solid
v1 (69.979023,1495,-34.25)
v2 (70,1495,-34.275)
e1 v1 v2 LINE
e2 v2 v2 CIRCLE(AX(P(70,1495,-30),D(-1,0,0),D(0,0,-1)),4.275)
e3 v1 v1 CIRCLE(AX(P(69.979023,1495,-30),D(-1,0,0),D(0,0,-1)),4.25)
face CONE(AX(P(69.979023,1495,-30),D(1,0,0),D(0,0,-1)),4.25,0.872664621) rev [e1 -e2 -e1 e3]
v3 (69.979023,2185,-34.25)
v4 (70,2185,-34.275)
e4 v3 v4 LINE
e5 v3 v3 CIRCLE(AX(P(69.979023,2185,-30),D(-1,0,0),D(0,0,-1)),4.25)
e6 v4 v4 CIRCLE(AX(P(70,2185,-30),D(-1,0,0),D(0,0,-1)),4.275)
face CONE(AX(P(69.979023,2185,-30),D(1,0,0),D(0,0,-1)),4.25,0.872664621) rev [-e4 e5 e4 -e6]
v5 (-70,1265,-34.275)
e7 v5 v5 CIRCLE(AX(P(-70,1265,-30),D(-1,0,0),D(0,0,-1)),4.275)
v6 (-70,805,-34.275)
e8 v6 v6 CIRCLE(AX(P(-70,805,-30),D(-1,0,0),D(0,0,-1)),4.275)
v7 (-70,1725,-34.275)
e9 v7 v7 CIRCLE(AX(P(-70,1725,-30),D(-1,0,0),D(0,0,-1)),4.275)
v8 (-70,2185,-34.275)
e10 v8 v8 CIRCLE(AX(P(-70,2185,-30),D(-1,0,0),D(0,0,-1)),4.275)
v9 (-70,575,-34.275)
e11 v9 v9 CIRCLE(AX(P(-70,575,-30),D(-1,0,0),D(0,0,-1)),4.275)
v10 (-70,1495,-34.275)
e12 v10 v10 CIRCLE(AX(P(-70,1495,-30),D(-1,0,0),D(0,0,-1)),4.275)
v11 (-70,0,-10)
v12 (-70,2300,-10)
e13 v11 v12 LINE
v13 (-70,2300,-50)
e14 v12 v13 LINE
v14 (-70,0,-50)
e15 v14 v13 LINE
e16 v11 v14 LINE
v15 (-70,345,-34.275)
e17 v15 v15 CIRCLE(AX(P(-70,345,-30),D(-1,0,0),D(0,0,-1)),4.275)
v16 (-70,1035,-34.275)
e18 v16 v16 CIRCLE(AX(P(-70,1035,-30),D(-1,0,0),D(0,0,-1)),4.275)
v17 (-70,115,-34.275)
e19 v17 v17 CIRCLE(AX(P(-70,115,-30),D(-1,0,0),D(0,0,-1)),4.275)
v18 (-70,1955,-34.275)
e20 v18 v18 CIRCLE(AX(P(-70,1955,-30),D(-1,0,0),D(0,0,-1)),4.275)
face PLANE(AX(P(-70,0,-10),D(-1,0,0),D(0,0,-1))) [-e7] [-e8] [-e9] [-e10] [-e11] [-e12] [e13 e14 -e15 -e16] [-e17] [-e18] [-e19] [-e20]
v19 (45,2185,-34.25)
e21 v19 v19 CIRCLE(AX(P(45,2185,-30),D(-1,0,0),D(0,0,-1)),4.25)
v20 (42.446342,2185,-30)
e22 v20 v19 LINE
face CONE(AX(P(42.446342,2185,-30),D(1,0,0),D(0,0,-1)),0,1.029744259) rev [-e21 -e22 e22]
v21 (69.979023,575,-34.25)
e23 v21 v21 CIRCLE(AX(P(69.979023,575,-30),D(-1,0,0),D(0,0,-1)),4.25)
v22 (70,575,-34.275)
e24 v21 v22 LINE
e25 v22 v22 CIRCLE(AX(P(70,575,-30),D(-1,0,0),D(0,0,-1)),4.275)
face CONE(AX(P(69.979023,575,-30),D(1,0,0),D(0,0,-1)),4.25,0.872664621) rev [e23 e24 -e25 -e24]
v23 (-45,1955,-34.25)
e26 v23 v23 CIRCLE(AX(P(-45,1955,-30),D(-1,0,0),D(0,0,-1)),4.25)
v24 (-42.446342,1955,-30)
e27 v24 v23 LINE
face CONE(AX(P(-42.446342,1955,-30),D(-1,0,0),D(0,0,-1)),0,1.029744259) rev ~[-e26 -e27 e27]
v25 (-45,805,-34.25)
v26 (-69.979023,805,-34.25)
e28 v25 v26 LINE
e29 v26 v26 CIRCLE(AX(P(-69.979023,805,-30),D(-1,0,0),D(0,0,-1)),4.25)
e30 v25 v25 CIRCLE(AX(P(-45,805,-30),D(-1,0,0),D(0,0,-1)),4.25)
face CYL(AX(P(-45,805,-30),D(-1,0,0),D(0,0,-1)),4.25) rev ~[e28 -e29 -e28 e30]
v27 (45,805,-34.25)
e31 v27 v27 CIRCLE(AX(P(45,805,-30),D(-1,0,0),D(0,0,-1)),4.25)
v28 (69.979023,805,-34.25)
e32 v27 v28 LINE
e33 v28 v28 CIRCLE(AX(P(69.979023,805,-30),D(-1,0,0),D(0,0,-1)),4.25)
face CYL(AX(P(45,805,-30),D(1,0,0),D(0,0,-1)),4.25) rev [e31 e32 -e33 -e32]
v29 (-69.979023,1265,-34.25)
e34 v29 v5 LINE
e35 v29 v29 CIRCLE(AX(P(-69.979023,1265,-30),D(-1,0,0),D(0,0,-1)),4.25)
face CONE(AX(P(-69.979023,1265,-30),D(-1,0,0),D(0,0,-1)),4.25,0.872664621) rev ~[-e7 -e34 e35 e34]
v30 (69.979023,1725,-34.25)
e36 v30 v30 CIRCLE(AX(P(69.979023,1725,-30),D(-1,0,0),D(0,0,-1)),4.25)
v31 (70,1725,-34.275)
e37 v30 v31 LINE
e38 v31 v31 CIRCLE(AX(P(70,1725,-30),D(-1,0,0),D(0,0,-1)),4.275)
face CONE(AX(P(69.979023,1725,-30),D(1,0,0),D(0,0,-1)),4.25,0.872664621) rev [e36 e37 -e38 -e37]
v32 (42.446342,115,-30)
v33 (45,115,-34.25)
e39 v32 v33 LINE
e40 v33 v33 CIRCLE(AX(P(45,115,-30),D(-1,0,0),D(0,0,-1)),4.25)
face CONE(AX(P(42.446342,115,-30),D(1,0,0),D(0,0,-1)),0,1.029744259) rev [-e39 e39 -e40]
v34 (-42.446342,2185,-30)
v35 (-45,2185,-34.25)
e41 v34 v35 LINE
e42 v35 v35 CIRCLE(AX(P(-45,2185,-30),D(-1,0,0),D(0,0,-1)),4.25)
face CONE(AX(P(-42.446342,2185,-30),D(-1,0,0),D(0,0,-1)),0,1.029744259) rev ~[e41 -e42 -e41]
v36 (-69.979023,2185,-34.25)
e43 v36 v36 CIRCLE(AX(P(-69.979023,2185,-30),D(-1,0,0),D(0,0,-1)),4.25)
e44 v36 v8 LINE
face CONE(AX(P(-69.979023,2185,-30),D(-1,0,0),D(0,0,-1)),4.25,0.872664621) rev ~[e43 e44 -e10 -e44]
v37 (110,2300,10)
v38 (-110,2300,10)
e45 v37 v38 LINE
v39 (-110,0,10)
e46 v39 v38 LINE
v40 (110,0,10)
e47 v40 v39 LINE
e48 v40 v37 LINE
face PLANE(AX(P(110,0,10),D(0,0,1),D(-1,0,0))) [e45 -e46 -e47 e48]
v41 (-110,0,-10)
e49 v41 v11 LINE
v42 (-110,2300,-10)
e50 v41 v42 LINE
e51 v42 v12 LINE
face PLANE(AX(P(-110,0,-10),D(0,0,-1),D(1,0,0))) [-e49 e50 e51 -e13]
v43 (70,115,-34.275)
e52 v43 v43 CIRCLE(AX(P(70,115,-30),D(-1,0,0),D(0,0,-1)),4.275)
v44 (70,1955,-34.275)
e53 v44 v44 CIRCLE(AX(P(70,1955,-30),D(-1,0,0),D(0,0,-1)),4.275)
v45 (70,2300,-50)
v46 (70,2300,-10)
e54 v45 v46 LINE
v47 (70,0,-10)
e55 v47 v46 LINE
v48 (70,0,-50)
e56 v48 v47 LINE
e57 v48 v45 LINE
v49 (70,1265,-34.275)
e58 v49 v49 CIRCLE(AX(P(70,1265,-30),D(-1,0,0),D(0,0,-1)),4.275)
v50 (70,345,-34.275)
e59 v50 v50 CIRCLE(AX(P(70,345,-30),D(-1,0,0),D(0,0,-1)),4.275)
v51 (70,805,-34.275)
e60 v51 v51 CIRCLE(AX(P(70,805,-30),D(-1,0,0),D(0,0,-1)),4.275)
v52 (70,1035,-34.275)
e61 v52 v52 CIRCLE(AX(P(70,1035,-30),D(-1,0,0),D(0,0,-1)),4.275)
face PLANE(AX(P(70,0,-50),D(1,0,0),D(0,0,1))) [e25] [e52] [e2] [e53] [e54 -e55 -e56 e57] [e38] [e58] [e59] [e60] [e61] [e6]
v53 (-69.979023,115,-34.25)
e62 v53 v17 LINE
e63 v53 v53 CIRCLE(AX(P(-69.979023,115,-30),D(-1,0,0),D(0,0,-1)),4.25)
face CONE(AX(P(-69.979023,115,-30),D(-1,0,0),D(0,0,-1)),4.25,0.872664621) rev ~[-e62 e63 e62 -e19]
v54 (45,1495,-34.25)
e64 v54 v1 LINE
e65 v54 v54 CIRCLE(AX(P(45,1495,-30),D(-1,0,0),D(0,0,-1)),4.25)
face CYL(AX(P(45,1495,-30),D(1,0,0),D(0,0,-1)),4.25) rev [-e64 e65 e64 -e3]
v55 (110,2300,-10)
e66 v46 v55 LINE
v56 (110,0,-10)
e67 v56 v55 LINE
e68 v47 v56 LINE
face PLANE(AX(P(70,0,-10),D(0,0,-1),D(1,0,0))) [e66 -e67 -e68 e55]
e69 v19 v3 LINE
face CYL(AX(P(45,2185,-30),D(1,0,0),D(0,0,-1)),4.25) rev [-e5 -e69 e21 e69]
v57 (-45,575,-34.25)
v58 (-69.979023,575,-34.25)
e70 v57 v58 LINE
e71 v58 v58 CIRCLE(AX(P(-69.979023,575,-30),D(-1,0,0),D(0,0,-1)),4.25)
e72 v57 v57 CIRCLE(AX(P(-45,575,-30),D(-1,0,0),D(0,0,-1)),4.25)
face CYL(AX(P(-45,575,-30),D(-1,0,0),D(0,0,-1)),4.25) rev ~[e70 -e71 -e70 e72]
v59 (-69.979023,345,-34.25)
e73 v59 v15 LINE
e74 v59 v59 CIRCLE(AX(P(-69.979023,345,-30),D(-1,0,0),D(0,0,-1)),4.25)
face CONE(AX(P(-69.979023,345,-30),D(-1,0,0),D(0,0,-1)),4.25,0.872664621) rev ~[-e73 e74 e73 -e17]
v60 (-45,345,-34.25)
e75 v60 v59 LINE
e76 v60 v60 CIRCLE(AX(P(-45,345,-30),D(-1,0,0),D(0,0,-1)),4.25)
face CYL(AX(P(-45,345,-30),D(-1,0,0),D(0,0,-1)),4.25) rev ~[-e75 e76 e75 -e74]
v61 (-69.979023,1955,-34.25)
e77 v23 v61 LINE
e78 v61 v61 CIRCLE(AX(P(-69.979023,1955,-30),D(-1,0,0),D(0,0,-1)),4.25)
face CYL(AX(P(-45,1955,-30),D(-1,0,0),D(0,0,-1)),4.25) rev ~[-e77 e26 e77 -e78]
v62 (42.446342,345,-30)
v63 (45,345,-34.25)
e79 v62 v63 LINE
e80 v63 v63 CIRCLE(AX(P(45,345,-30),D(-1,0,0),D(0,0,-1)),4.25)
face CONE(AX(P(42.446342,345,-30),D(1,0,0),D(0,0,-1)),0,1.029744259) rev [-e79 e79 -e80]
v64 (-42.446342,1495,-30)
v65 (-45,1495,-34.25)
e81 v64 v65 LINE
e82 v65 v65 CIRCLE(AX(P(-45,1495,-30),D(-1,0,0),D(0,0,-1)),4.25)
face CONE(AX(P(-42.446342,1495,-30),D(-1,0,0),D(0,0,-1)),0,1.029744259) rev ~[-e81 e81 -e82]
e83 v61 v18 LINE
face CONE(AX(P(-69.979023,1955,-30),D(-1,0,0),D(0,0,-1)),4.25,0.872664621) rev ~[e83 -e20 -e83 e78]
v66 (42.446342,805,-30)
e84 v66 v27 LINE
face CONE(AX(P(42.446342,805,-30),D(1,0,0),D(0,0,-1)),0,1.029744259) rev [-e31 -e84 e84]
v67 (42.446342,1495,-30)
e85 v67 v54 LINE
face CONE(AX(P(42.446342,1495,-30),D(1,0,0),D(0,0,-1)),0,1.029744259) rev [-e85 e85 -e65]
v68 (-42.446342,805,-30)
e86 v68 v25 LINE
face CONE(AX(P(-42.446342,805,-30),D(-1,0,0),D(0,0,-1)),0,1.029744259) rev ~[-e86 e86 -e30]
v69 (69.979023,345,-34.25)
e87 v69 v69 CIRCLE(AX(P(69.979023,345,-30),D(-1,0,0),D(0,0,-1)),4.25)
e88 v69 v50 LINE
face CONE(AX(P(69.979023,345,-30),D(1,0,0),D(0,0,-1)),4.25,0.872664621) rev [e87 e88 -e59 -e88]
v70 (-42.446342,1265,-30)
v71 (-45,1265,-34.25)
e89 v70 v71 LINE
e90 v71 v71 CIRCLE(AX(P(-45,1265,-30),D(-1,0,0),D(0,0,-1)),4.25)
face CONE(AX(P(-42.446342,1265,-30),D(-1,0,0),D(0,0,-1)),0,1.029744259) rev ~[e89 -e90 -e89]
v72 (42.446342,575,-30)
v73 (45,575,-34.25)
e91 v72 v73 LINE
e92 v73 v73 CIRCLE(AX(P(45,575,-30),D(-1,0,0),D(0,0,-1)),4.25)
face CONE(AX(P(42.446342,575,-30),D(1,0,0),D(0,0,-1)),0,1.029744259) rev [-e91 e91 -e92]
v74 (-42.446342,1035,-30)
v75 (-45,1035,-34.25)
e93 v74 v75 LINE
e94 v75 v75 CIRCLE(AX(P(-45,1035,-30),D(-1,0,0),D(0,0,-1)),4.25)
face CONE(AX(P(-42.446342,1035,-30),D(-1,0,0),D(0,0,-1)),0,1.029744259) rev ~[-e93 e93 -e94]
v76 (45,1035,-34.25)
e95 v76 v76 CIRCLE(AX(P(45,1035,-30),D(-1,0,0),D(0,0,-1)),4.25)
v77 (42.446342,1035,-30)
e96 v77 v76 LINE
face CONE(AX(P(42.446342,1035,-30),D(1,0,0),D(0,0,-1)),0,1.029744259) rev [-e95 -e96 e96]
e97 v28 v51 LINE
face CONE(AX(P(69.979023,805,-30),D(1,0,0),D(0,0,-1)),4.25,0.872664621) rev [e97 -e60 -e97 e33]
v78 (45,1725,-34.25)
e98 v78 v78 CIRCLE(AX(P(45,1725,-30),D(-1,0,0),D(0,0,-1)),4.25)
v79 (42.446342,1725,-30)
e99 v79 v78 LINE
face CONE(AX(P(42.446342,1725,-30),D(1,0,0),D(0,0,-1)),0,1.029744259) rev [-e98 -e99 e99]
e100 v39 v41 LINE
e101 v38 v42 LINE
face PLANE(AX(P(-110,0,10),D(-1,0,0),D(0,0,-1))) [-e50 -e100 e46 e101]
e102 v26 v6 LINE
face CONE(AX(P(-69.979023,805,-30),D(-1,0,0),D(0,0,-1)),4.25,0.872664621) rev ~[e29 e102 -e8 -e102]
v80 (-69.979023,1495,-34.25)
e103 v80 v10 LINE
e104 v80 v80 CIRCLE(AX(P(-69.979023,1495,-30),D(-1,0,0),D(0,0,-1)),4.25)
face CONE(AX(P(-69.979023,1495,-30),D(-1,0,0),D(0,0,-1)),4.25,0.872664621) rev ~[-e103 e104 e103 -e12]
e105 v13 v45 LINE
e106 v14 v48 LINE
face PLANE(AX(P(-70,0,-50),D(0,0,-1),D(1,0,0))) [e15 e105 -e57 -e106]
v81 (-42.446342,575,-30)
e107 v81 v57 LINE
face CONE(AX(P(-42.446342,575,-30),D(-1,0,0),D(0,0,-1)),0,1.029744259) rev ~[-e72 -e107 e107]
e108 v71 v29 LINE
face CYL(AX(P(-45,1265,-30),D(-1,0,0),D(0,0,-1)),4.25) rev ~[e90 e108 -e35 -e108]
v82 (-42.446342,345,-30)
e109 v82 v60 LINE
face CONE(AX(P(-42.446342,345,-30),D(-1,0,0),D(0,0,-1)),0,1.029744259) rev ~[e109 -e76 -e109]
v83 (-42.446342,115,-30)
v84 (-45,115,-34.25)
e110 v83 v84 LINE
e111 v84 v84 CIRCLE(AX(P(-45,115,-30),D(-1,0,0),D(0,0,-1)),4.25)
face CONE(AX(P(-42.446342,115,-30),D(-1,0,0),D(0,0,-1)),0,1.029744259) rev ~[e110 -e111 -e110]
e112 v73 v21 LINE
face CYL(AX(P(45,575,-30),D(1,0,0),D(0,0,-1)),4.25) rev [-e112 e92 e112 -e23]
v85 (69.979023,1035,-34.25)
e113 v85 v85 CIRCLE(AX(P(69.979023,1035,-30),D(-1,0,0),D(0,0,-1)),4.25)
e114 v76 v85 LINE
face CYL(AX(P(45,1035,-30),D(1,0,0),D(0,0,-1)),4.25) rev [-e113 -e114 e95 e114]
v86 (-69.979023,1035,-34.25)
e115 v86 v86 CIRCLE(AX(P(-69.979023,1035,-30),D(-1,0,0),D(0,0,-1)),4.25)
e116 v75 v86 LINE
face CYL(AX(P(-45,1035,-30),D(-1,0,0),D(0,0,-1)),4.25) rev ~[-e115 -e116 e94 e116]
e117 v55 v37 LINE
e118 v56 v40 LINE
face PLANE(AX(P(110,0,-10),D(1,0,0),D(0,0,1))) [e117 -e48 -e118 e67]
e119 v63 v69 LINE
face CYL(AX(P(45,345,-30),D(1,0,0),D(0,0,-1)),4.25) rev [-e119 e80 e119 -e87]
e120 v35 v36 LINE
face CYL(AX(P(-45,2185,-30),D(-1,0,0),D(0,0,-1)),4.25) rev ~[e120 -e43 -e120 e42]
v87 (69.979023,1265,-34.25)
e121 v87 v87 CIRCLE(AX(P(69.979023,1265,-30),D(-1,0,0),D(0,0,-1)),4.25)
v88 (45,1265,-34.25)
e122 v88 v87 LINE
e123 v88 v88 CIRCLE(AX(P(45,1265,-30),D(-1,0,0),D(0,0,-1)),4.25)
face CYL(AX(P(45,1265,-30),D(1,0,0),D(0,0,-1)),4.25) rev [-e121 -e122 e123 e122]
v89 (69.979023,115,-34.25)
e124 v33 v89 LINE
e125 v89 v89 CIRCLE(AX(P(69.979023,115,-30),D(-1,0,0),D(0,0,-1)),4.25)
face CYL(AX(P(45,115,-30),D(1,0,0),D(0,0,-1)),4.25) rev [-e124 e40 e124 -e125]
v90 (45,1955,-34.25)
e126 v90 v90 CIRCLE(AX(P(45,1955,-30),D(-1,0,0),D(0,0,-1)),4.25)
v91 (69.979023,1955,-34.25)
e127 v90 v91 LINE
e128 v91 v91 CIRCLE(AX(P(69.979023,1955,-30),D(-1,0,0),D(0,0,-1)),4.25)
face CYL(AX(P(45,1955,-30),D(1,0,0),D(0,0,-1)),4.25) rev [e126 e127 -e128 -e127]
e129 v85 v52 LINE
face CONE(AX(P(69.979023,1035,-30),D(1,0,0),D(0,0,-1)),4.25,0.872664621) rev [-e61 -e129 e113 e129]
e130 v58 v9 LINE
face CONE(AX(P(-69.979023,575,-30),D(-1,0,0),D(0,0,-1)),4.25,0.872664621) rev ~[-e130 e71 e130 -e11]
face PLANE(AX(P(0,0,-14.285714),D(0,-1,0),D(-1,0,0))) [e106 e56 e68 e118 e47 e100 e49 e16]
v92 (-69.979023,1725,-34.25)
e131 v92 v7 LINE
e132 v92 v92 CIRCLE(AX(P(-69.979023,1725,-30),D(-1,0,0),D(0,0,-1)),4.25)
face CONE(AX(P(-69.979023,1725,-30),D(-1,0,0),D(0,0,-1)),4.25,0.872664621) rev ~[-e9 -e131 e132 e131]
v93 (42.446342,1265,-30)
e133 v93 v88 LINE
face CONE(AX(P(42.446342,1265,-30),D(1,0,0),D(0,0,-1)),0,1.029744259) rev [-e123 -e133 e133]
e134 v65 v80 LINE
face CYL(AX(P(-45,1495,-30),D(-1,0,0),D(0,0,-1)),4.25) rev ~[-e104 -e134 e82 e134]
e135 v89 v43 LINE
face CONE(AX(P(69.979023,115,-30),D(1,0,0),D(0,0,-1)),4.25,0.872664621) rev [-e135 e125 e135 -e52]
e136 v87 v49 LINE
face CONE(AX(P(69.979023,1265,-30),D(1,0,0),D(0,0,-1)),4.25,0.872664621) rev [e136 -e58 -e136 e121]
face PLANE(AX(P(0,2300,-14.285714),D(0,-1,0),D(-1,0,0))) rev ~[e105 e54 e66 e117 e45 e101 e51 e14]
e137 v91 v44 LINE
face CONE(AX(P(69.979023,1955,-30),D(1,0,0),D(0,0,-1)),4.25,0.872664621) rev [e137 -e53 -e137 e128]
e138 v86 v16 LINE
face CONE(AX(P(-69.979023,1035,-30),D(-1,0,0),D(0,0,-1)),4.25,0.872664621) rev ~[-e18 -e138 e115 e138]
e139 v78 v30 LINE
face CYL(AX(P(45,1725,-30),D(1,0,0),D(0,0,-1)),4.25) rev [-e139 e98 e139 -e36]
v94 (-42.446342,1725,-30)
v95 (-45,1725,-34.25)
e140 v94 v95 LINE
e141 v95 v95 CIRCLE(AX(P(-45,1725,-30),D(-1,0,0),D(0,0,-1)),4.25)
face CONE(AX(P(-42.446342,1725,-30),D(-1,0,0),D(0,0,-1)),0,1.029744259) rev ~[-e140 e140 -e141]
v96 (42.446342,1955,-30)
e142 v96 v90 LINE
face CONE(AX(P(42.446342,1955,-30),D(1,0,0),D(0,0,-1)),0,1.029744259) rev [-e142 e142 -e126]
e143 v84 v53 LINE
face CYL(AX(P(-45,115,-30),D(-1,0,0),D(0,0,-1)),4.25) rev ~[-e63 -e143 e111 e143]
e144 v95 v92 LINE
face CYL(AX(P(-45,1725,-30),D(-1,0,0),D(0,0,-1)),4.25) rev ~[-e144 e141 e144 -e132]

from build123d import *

# Parameters (mm, degrees)
BOSS_EXTRUDE1_DEPTH = 2300
LPATTERN1_COUNT     = 10
LPATTERN1_PITCH     = 230


with BuildPart() as part:
    # Sketch1 → Boss-Extrude1 (new body)
    with BuildSketch(Plane(origin=(0, 0, 0), x_dir=(1, 0, 0), z_dir=(0, 1, 0))):
        Polygon((-70, 10), (-70, 50), (70, 50), (70, 10), (110, 10), (110, -10), (-110, -10), (-110, 10), align=None)
    extrude(amount=BOSS_EXTRUDE1_DEPTH)

    # Sketch3 → Tap Drill for M10 Tap1 (revolve, cut)
    with BuildSketch(Plane(origin=(70, 2185, -30), x_dir=(0, 0, -1), z_dir=(0, 1, 0))):
        Polygon((0, 0), (0, 27.553657631), (4.25, 25), (4.25, 0.020977491), (4.275, 0), align=None)
    tap_drill_for_m10_tap1 = revolve(axis=Axis((76.35, 2185, -30), (-1, 0, 0)), mode=Mode.SUBTRACT)

    # LPattern1: Tap Drill for M10 Tap1 ×10
    with Locations(*[(0, -i * LPATTERN1_PITCH, 0) for i in range(1, LPATTERN1_COUNT)]):
        add(tap_drill_for_m10_tap1, mode=Mode.SUBTRACT)

    # Mirror1: Tap Drill for M10 Tap1 across plane
    add(tap_drill_for_m10_tap1.mirror(Plane(origin=(0, 0, 0), x_dir=(0, 0, 1), z_dir=(1, 0, 0))), mode=Mode.SUBTRACT)

    # Mirror1 copy 1 sketch → Mirror1 copy 1 (revolve, cut)
    with BuildSketch(Plane(origin=(-70, 1955, -30), x_dir=(0, 0, -1), z_dir=(0, 1, 0))):
        Polygon((0, 0), (0, -27.553657631), (4.25, -25), (4.25, -0.020977491), (4.275, 0), align=None)
    revolve(axis=Axis((-76.35, 1955, -30), (-1, 0, 0)), mode=Mode.SUBTRACT)

    # Mirror1 copy 2 sketch → Mirror1 copy 2 (revolve, cut)
    with BuildSketch(Plane(origin=(-70, 1725, -30), x_dir=(0, 0, -1), z_dir=(0, 1, 0))):
        Polygon((0, 0), (0, -27.553657631), (4.25, -25), (4.25, -0.020977491), (4.275, 0), align=None)
    revolve(axis=Axis((-76.35, 1725, -30), (-1, 0, 0)), mode=Mode.SUBTRACT)

    # Mirror1 copy 3 sketch → Mirror1 copy 3 (revolve, cut)
    with BuildSketch(Plane(origin=(-70, 1495, -30), x_dir=(0, 0, -1), z_dir=(0, 1, 0))):
        Polygon((0, 0), (0, -27.553657631), (4.25, -25), (4.25, -0.020977491), (4.275, 0), align=None)
    revolve(axis=Axis((-76.35, 1495, -30), (-1, 0, 0)), mode=Mode.SUBTRACT)

    # Mirror1 copy 4 sketch → Mirror1 copy 4 (revolve, cut)
    with BuildSketch(Plane(origin=(-70, 1265, -30), x_dir=(0, 0, -1), z_dir=(0, 1, 0))):
        Polygon((0, 0), (0, -27.553657631), (4.25, -25), (4.25, -0.020977491), (4.275, 0), align=None)
    revolve(axis=Axis((-76.35, 1265, -30), (-1, 0, 0)), mode=Mode.SUBTRACT)

    # Mirror1 copy 5 sketch → Mirror1 copy 5 (revolve, cut)
    with BuildSketch(Plane(origin=(-70, 1035, -30), x_dir=(0, 0, -1), z_dir=(0, 1, 0))):
        Polygon((0, 0), (0, -27.553657631), (4.25, -25), (4.25, -0.020977491), (4.275, 0), align=None)
    revolve(axis=Axis((-76.35, 1035, -30), (-1, 0, 0)), mode=Mode.SUBTRACT)

    # Mirror1 copy 6 sketch → Mirror1 copy 6 (revolve, cut)
    with BuildSketch(Plane(origin=(-70, 805, -30), x_dir=(0, 0, -1), z_dir=(0, 1, 0))):
        Polygon((0, 0), (0, -27.553657631), (4.25, -25), (4.25, -0.020977491), (4.275, 0), align=None)
    revolve(axis=Axis((-76.35, 805, -30), (-1, 0, 0)), mode=Mode.SUBTRACT)

    # Mirror1 copy 7 sketch → Mirror1 copy 7 (revolve, cut)
    with BuildSketch(Plane(origin=(-70, 575, -30), x_dir=(0, 0, -1), z_dir=(0, 1, 0))):
        Polygon((0, 0), (0, -27.553657631), (4.25, -25), (4.25, -0.020977491), (4.275, 0), align=None)
    revolve(axis=Axis((-76.35, 575, -30), (-1, 0, 0)), mode=Mode.SUBTRACT)

    # Mirror1 copy 8 sketch → Mirror1 copy 8 (revolve, cut)
    with BuildSketch(Plane(origin=(-70, 345, -30), x_dir=(0, 0, -1), z_dir=(0, 1, 0))):
        Polygon((0, 0), (0, -27.553657631), (4.25, -25), (4.25, -0.020977491), (4.275, 0), align=None)
    revolve(axis=Axis((-76.35, 345, -30), (-1, 0, 0)), mode=Mode.SUBTRACT)

    # Mirror1 copy 9 sketch → Mirror1 copy 9 (revolve, cut)
    with BuildSketch(Plane(origin=(-70, 115, -30), x_dir=(0, 0, -1), z_dir=(0, 1, 0))):
        Polygon((0, 0), (0, -27.553657631), (4.25, -25), (4.25, -0.020977491), (4.275, 0), align=None)
    revolve(axis=Axis((-76.35, 115, -30), (-1, 0, 0)), mode=Mode.SUBTRACT)


solid = part.part
